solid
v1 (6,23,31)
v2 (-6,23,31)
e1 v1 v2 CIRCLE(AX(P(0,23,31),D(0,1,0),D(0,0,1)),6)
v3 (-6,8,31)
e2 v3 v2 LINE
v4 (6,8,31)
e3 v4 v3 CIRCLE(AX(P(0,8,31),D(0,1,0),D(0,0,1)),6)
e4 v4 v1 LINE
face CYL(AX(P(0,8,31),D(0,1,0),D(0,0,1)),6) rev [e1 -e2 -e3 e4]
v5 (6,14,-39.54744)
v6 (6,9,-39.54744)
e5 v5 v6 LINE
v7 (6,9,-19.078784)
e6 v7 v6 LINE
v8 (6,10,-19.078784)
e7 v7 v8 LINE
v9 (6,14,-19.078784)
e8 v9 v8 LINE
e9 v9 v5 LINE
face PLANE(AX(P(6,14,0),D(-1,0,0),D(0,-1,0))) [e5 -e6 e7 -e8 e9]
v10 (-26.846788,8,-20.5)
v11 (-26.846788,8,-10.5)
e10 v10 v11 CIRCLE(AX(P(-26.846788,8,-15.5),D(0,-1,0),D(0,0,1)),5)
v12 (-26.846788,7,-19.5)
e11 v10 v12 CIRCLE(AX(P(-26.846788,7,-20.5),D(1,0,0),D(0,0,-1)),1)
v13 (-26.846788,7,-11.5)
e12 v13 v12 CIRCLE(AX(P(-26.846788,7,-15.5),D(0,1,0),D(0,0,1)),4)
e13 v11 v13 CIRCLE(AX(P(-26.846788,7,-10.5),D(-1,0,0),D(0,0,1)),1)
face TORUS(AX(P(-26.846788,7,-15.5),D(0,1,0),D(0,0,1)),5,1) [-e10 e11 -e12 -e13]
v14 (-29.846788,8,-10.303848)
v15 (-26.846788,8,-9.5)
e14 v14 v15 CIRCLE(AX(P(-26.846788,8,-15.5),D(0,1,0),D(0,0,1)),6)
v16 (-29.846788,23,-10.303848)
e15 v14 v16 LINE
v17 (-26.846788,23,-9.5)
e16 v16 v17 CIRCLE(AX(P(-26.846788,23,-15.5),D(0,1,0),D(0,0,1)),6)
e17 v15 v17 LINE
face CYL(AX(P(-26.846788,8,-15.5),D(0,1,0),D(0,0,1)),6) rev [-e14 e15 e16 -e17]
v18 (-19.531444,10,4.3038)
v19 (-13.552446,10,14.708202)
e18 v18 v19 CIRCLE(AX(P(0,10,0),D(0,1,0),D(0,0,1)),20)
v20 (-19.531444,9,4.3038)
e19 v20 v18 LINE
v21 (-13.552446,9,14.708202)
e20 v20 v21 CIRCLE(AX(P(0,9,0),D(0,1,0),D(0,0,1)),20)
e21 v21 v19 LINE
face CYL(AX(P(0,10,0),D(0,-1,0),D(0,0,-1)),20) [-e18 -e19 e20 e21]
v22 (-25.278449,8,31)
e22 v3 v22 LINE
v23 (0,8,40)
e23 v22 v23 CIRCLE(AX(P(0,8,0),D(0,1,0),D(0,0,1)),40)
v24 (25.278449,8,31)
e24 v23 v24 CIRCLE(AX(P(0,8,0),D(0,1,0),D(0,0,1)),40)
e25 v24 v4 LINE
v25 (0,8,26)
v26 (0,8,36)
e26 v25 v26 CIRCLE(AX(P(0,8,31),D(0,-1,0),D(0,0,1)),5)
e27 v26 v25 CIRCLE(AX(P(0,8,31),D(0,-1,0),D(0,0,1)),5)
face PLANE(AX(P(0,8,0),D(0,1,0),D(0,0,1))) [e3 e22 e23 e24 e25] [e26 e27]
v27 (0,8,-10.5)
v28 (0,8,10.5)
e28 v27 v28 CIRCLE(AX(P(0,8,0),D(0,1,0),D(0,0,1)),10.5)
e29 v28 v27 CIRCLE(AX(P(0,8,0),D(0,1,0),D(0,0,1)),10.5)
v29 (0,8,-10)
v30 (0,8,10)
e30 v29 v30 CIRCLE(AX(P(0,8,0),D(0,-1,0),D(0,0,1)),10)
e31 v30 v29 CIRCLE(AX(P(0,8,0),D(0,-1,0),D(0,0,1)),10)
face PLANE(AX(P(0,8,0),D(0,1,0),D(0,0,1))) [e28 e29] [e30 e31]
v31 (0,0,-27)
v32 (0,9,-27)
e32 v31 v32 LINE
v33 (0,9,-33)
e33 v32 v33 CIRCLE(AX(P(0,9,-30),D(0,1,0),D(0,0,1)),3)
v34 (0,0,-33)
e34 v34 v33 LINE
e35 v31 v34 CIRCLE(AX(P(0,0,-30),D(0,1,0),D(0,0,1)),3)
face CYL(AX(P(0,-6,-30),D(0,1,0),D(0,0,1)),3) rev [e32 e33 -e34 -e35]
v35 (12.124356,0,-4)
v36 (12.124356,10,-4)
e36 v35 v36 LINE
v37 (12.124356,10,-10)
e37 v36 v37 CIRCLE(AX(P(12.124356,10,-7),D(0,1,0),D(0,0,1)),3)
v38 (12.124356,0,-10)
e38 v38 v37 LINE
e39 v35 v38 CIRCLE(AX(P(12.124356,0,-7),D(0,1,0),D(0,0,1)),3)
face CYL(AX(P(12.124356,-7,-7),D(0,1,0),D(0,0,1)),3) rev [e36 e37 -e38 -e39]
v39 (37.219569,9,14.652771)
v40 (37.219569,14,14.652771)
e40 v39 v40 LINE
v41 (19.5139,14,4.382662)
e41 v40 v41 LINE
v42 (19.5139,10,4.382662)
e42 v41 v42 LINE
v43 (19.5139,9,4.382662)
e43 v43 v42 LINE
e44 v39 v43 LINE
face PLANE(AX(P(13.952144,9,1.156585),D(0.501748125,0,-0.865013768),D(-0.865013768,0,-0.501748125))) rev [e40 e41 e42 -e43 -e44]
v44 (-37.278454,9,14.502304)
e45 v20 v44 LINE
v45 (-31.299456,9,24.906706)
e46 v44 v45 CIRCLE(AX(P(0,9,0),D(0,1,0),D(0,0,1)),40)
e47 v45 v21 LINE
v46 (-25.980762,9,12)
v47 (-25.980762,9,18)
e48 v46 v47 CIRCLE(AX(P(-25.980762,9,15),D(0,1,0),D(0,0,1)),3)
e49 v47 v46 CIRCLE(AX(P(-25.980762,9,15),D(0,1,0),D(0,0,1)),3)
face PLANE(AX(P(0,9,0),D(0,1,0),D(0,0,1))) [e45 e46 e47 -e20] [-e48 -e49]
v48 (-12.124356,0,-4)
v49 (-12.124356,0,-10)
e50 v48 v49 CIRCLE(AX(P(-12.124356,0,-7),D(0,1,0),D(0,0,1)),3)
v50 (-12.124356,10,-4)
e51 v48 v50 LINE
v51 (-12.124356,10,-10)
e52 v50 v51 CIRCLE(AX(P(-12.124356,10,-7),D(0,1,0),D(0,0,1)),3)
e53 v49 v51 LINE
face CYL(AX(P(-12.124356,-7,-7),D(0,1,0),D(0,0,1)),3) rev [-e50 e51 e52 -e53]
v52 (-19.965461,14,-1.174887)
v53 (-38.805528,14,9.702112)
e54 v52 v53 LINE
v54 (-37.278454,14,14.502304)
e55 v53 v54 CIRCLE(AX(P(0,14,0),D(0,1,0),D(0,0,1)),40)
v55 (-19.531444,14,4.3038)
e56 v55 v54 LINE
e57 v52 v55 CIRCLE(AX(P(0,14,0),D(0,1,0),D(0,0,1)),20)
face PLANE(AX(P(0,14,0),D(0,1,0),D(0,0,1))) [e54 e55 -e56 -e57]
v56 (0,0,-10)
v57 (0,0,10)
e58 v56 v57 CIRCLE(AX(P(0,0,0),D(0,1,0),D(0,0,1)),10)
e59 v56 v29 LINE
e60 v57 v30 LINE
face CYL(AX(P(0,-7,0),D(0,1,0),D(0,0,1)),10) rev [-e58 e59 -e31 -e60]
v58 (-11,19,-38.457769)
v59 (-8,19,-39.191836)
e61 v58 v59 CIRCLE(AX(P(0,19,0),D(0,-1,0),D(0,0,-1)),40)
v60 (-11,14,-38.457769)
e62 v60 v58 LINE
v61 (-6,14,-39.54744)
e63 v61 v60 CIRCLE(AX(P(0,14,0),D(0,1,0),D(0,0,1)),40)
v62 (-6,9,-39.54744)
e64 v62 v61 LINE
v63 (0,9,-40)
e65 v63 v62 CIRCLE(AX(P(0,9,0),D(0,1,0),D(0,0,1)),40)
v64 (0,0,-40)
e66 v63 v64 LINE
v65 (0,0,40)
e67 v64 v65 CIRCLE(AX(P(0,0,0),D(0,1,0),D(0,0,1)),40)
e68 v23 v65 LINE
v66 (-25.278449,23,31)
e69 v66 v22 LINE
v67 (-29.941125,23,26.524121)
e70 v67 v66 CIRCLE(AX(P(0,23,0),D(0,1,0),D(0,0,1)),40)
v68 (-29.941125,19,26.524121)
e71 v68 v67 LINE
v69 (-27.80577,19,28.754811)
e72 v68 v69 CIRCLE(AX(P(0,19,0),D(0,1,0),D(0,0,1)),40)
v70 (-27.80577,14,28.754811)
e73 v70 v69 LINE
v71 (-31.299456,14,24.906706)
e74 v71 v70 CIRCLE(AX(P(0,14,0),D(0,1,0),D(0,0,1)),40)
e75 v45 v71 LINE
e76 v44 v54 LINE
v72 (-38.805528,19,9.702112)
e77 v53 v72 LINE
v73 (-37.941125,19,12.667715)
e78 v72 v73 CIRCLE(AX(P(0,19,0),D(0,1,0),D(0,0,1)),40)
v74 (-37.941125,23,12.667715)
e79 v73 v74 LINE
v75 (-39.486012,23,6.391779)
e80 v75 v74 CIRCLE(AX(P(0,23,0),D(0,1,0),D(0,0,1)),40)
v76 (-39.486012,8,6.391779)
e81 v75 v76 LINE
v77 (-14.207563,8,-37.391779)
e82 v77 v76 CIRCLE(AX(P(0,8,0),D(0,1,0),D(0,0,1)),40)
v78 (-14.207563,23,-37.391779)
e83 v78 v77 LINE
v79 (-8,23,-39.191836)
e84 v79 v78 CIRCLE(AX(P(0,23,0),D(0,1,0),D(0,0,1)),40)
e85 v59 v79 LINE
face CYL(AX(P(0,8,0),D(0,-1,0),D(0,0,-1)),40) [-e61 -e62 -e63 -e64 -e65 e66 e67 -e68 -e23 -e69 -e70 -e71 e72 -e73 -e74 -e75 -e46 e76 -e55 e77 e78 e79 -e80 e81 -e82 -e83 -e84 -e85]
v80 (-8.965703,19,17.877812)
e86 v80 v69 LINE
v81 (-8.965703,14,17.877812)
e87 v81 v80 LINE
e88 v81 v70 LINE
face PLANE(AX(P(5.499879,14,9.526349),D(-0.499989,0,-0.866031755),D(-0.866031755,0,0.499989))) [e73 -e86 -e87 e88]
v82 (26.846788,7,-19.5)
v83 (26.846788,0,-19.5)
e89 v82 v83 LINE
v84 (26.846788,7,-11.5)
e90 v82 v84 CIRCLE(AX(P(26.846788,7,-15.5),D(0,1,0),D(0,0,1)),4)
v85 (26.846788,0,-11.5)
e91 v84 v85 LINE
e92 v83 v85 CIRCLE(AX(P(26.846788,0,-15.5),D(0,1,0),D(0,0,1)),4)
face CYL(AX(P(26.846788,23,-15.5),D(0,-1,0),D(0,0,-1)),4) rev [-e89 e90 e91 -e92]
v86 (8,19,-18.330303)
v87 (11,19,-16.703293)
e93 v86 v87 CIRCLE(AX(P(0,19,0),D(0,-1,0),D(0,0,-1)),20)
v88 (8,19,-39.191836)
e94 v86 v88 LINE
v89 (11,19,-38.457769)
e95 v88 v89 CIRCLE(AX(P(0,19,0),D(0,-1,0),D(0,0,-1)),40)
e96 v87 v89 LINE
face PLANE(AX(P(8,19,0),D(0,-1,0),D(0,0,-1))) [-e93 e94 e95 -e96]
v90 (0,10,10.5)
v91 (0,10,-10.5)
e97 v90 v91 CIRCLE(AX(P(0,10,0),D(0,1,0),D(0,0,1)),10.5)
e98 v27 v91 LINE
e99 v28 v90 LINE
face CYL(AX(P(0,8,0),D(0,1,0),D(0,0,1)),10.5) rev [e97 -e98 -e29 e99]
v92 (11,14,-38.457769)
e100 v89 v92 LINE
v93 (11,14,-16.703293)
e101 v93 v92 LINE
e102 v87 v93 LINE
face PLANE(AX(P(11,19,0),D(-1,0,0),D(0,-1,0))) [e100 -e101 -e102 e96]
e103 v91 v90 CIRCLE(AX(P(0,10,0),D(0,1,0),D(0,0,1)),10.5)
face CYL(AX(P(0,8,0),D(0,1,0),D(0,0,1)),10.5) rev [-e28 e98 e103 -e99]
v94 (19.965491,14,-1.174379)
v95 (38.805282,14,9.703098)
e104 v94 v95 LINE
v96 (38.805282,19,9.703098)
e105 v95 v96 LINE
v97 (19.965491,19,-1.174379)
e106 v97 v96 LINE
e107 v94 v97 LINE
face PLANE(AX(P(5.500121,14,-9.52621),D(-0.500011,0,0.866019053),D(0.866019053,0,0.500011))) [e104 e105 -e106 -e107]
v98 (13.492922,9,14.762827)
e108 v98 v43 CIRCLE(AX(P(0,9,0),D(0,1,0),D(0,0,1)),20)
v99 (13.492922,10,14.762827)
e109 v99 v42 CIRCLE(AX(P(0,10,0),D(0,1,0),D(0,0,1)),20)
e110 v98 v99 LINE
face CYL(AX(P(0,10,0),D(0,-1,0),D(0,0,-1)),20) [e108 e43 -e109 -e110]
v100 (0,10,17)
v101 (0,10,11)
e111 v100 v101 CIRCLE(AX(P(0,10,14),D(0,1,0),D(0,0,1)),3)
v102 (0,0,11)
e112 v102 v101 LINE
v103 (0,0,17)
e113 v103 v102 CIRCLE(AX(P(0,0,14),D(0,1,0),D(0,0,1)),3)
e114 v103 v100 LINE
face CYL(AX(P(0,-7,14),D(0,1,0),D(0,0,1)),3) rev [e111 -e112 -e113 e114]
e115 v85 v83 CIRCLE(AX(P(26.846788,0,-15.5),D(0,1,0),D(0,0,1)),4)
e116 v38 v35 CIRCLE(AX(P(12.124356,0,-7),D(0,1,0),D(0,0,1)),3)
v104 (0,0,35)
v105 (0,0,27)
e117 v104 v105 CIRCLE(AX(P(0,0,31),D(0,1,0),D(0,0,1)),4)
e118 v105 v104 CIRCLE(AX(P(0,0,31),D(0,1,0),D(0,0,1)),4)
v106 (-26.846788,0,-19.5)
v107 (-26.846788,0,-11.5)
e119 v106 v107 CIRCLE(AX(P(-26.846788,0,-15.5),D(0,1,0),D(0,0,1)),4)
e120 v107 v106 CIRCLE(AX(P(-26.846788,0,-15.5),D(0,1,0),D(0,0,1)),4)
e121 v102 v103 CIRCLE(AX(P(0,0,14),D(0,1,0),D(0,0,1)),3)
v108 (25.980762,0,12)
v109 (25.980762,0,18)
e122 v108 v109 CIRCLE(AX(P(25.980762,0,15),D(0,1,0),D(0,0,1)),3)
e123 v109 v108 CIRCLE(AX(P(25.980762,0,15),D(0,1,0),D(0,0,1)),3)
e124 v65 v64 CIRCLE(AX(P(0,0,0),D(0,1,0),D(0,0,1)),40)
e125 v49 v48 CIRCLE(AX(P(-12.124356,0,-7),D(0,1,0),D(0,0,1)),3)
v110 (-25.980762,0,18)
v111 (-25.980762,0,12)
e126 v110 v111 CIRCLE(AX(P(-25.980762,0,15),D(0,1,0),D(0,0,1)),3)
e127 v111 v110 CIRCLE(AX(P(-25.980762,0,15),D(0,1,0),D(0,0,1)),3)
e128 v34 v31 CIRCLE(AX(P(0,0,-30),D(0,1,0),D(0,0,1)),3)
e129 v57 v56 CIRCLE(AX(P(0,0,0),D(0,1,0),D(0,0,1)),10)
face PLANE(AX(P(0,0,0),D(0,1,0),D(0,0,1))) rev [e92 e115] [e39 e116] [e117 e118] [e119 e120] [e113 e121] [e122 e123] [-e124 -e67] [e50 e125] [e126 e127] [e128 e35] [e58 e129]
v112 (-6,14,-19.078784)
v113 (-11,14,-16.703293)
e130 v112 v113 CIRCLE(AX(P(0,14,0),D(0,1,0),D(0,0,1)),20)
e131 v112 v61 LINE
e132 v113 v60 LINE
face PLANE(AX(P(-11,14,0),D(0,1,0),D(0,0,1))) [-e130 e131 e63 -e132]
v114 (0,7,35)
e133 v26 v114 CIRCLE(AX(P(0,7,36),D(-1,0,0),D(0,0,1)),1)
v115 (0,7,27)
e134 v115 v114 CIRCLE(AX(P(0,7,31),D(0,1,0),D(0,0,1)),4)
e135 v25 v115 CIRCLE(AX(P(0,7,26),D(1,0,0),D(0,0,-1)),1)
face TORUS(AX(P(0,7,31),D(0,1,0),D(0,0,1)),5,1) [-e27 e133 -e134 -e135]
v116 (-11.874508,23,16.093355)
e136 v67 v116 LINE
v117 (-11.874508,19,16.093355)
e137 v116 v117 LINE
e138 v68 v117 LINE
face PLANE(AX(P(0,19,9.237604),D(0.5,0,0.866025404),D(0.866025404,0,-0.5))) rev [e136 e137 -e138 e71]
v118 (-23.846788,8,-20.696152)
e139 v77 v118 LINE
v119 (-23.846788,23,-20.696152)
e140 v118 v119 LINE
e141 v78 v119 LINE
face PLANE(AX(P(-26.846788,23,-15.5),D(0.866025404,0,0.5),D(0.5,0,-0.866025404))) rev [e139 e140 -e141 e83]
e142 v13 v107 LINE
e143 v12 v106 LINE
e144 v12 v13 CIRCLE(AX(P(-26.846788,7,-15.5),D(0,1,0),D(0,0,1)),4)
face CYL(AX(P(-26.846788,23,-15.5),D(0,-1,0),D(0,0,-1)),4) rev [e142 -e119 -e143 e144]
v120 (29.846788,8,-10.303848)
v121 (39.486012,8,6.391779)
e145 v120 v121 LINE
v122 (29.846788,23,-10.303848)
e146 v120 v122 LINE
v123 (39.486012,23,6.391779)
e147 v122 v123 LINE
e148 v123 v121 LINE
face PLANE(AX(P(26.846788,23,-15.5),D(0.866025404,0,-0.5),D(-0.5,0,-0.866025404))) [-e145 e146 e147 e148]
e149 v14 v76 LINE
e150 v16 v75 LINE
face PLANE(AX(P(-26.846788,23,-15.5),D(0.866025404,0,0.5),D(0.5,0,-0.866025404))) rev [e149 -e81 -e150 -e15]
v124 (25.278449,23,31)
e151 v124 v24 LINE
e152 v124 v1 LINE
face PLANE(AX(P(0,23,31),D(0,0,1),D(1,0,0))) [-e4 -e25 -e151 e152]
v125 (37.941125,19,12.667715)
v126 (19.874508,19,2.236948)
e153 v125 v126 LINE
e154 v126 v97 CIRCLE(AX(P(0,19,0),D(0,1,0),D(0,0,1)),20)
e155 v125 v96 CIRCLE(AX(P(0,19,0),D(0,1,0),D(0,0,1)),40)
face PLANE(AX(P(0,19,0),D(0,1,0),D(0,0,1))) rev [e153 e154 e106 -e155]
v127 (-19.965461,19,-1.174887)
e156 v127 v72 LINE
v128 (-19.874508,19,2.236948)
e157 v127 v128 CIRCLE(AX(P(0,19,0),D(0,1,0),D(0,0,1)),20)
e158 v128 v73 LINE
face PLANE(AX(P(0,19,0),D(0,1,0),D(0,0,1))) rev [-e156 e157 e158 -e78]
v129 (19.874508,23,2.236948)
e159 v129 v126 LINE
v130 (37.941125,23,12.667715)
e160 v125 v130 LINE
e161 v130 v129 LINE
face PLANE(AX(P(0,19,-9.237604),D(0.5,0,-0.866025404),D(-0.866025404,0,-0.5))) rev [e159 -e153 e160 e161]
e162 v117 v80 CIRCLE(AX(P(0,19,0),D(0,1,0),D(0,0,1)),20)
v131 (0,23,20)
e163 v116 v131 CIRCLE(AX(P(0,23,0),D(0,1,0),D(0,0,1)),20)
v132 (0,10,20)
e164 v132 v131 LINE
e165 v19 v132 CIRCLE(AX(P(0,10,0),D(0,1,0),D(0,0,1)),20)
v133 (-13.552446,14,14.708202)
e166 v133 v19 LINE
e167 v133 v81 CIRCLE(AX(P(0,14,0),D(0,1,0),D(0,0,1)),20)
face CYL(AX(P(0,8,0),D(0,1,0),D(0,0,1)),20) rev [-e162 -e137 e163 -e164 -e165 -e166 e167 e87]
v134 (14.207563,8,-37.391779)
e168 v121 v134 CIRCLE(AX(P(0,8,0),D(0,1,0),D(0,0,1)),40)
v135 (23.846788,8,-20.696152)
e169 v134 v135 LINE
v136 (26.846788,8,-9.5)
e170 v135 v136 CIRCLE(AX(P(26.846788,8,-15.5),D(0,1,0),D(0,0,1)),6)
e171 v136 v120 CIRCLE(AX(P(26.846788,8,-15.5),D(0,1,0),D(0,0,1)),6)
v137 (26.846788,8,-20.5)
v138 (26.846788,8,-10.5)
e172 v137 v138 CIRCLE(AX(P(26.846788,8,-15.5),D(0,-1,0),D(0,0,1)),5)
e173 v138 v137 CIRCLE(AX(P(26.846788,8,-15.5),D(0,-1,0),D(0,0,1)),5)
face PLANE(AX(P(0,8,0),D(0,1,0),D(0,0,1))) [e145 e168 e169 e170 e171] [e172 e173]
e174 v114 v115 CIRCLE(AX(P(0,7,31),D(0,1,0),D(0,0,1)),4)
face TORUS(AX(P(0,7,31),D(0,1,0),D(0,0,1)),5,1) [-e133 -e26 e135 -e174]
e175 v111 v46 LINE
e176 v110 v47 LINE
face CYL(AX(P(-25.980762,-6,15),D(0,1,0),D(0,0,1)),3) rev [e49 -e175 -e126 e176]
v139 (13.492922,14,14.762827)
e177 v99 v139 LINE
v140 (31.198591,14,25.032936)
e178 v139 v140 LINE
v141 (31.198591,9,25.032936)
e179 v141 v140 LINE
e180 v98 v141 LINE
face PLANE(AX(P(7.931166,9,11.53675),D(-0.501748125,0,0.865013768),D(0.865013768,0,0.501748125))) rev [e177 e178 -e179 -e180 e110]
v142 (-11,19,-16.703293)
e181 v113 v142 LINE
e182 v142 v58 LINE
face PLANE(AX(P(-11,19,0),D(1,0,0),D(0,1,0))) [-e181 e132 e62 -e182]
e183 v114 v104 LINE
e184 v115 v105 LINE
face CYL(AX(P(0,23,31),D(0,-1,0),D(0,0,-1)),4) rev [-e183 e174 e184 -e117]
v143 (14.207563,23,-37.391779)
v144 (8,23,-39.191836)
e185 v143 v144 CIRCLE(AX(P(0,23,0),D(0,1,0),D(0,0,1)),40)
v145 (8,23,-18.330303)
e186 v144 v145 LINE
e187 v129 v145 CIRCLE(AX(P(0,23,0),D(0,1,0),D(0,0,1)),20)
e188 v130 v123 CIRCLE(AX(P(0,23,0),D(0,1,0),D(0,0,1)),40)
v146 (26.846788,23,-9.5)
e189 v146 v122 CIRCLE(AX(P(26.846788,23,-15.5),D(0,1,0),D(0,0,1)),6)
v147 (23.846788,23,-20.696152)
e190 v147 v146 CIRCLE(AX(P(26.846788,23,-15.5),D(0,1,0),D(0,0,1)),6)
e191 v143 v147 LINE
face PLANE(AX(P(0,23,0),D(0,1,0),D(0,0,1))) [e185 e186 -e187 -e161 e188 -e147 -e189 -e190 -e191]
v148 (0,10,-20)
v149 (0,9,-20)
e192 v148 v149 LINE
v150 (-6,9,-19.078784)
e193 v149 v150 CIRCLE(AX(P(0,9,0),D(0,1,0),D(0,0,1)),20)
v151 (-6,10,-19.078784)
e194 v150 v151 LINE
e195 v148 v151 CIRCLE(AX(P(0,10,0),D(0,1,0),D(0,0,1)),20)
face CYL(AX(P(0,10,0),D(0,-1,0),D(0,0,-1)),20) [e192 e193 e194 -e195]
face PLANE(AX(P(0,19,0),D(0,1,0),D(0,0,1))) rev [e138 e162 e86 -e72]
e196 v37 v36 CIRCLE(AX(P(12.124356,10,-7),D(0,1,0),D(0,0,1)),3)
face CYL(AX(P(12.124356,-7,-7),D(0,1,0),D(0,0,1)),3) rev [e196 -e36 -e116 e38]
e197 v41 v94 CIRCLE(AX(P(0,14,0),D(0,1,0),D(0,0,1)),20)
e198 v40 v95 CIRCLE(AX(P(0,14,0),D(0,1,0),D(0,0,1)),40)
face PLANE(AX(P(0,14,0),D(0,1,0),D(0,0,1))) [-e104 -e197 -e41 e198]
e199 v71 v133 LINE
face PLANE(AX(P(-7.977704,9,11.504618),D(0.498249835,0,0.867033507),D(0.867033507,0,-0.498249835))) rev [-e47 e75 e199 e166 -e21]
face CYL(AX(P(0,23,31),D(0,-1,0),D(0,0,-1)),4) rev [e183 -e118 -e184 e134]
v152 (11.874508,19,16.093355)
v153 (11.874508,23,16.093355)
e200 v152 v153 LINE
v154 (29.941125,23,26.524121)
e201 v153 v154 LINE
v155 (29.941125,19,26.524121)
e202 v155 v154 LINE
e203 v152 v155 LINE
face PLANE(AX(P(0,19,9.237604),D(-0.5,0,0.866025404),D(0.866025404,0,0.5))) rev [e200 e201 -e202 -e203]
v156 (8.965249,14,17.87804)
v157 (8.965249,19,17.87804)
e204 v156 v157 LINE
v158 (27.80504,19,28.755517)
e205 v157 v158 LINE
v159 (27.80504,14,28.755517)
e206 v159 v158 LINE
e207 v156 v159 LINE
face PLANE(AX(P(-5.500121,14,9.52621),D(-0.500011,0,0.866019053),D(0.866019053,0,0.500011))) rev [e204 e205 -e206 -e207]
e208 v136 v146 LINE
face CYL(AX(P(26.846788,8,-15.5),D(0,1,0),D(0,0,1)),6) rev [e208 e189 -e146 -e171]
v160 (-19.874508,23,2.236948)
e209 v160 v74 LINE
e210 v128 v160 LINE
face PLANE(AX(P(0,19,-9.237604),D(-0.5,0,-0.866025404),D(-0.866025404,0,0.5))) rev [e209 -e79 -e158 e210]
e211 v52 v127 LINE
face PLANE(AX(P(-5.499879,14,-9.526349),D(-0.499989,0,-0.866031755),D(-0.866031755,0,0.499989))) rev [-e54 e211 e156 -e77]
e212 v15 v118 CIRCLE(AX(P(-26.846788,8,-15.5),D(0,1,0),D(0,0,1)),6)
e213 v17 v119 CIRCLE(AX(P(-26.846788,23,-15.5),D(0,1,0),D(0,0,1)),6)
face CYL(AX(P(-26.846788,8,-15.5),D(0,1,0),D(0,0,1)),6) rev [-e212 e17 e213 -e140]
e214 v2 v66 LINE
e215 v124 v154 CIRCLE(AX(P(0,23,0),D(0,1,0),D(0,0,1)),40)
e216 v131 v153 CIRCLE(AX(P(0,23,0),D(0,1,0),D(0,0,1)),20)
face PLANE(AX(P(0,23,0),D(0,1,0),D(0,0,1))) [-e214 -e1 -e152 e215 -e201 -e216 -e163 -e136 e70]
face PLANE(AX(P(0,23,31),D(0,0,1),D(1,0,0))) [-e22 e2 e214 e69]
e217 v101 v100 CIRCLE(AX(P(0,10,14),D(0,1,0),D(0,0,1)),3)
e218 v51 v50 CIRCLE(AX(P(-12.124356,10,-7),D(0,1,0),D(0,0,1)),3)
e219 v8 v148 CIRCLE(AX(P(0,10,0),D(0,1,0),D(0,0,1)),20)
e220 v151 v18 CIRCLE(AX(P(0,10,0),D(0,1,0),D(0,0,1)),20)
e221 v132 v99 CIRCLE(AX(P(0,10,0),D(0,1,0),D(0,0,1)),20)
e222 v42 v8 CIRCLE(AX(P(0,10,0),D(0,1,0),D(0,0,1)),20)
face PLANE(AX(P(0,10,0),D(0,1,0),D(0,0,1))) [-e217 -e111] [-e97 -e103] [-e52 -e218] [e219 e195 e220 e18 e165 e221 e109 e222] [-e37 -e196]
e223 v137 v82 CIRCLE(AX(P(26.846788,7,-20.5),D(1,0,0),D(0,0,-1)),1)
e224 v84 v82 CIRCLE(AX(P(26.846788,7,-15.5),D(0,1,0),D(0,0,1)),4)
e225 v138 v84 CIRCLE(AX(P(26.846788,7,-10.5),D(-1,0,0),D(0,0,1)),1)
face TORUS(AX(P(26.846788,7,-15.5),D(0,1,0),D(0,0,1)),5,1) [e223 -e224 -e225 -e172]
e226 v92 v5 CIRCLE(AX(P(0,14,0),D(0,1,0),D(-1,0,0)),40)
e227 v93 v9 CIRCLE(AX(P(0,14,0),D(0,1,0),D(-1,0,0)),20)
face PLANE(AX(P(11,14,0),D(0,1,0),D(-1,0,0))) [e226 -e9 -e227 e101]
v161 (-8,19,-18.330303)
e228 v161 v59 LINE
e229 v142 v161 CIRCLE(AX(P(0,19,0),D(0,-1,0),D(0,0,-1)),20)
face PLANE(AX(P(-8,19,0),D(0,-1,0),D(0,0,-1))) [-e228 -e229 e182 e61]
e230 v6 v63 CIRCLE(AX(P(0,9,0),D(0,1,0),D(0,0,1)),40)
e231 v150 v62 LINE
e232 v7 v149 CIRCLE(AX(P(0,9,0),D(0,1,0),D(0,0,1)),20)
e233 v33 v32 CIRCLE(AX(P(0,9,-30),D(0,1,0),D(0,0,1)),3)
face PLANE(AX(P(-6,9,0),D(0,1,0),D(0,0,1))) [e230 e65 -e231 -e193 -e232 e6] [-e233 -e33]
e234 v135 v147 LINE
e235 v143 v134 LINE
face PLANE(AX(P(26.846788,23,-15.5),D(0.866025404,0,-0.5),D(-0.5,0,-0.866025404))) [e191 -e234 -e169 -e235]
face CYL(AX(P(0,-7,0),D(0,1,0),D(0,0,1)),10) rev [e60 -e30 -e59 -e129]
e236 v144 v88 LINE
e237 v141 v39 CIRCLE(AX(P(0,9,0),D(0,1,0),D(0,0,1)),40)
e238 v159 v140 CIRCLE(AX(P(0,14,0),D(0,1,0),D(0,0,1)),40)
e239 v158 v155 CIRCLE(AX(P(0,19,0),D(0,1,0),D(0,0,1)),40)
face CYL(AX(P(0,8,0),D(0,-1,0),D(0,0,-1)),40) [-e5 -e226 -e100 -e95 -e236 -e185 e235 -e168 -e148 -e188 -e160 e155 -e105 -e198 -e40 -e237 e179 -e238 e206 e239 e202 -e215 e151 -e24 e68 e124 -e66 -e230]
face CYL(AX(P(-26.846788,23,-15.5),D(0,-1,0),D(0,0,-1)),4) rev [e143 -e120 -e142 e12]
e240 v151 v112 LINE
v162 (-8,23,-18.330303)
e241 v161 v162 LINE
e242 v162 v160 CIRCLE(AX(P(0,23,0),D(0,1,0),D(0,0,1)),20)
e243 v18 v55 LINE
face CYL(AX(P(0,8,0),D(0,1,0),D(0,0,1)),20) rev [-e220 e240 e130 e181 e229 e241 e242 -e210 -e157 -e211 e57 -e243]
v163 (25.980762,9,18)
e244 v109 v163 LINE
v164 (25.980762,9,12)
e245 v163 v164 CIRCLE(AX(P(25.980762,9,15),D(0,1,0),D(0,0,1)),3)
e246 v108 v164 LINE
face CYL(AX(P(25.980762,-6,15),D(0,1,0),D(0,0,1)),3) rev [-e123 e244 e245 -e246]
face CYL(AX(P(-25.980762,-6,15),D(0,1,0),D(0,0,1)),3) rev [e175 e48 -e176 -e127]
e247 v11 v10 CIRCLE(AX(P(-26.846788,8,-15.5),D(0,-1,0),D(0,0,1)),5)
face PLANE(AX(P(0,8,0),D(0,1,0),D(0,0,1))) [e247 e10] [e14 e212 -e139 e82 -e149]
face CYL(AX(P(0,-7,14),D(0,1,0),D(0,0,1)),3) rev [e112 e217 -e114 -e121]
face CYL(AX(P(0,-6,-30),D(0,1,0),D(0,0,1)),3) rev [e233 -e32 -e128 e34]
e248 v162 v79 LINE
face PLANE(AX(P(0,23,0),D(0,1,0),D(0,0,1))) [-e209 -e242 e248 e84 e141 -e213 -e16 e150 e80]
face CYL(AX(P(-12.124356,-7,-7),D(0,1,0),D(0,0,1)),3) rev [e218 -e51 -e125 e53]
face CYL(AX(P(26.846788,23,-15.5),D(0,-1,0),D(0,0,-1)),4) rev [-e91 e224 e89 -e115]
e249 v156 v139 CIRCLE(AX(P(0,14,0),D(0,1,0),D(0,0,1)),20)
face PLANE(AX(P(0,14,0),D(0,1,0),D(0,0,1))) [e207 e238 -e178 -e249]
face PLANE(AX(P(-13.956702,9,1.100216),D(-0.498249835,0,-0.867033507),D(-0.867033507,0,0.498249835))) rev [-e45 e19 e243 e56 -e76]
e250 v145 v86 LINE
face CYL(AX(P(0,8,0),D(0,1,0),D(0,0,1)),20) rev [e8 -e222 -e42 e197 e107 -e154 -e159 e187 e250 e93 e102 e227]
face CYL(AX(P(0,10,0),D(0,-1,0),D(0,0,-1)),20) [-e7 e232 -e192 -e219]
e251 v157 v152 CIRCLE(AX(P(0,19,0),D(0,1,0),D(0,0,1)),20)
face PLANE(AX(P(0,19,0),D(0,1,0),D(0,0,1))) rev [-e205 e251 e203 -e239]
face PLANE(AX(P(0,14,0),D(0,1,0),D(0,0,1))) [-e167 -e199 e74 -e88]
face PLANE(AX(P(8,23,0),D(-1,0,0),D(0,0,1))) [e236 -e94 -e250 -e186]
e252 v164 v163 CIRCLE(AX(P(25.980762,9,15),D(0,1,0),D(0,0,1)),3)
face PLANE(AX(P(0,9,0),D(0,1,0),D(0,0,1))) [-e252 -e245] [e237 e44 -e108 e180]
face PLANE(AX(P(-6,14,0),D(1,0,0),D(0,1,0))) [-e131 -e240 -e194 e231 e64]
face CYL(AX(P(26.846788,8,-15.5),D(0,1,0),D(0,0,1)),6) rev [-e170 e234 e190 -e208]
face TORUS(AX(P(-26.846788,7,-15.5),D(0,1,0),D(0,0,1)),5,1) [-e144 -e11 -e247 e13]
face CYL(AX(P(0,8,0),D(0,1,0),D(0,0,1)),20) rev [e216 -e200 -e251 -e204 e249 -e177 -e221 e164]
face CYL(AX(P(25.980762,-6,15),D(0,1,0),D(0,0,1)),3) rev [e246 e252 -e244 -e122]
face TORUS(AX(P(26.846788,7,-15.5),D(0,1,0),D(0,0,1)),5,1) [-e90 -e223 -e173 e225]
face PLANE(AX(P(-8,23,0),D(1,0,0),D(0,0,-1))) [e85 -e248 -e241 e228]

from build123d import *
from build123d.topology import SkipClean

# Parameters (mm, degrees)
FLANGE_DISC_SKETCH_R           = 40
FLANGE_DISC_80_DEPTH           = 8
JAW_GUIDE_BOSSES_SKETCH_R      = 14
JAW_GUIDE_BOSSES_DEPTH         = 15
TRIANGULAR_START               = -30
TRIANGULAR_CENTRE_CUT_SKETCH_R = 4
TRIANGULAR_CENTRE_CUT_DEPTH    = 30
HEX_CUT_DEPTH                  = 15
JAW_SLOT_PROFILE_CUT_DEPTH     = 40
JAW_START                      = -4
JAW_POCKET_CUT_DEPTH           = 4
JAW_START_2                    = -5
JAW_GROOVE_CUT_A_DEPTH         = 5
JAW_GROOVE_CUT_B_DEPTH         = 5
CENTRE_BORE_SKETCH_R           = 20
CENTRE_BORE_40_DEPTH           = 15
THROUGH_BORE_SKETCH_R          = 10
THROUGH_BORE_20_DEPTH          = 15
FLANGE_HOLES_SKETCH_R          = 3
FLANGE_HOLES_3X_6_DEPTH        = 15
HUB_START                      = 2
HUB_RING_SKETCH_R              = 20
HUB_RING_SKETCH_R_2            = 10
HUB_RING_SKETCH_R_3            = 3
HUB_RING_DEPTH                 = 2
EDGE_FILLET_R1_A_R             = 1
EDGE_FILLET_R1_B_R             = 1
JAW_HOLES_SKETCH_R             = 3
JAW_HOLES_3X_6_DEPTH           = 15
COUNTERBORE_SKETCH_R           = 10.5
COUNTERBORE_21_DEPTH           = 2


with BuildPart() as part:
    # Flange Disc Sketch → Flange Disc Ø80 (new body)
    with BuildSketch(Plane(origin=(0, 0, 0), x_dir=(1, 0, 0), z_dir=(0, 1, 0))):
        with Locations(Location((0, 0, 0), (0, 0, 270))):
            Circle(FLANGE_DISC_SKETCH_R)
    extrude(amount=FLANGE_DISC_80_DEPTH)

    # Jaw Guide Bosses Sketch → Jaw Guide Bosses (add)
    with BuildSketch(Plane(origin=(0, 8, 0), x_dir=(1, 0, 0), z_dir=(0, 1, 0))):
        with BuildLine():
            ThreePointArc((-22.846787517, 15.5), (-24.846787517, 12.035898385), (-28.846787517, 12.035898385))
            Line((-28.846787517, 12.035898385), (-39.486012177, -6.391779279))
            ThreePointArc((-39.486012177, -6.391779279), (-34.641016151, -20), (-25.27844932, -31))
            Line((-25.27844932, -31), (-4, -31))
            ThreePointArc((-4, -31), (0, -27), (4, -31))
            Line((4, -31), (25.27844932, -31))
            ThreePointArc((25.27844932, -31), (34.641016151, -20), (39.486012177, -6.391779279))
            Line((39.486012177, -6.391779279), (28.846787517, 12.035898385))
            ThreePointArc((28.846787517, 12.035898385), (23.382685902, 13.5), (24.846787517, 18.964101615))
            Line((24.846787517, 18.964101615), (14.207562858, 37.391779279))
            ThreePointArc((14.207562858, 37.391779279), (0, 40), (-14.207562858, 37.391779279))
            Line((-14.207562858, 37.391779279), (-24.846787517, 18.964101615))
            ThreePointArc((-24.846787517, 18.964101615), (-23.382685902, 17.5), (-22.846787517, 15.5))
        make_face()
        with Locations(Location((0, 0, 0), (0, 0, 270))):
            Circle(JAW_GUIDE_BOSSES_SKETCH_R, mode=Mode.SUBTRACT)
    extrude(amount=JAW_GUIDE_BOSSES_DEPTH)

    # Triangular Centre Cut Sketch → Triangular Centre Cut (cut)
    with SkipClean():  # the faces are left unmerged after this step: merging them gives an invalid solid
        with BuildSketch(Plane(origin=(0, 23, 0), x_dir=(1, 0, 0), z_dir=(0, 1, 0)).offset(TRIANGULAR_START)):
            with Locations(Location((-26.846787517, 15.5, 0), (0, 0, 60))):
                Circle(TRIANGULAR_CENTRE_CUT_SKETCH_R)
            with Locations(Location((26.846787517, 15.5, 0), (0, 0, 120))):
                Circle(TRIANGULAR_CENTRE_CUT_SKETCH_R)
            with Locations((0, -31)):
                Circle(TRIANGULAR_CENTRE_CUT_SKETCH_R)
        extrude(amount=TRIANGULAR_CENTRE_CUT_DEPTH, mode=Mode.SUBTRACT)

    # Hex Cut Sketch → Hex Cut (cut)
    with BuildSketch(Plane(origin=(0, 23, 0), x_dir=(1, 0, 0), z_dir=(0, 1, 0))):
        with BuildLine():
            Line((-29.846787517, 10.303847577), (-23.846787517, 20.696152423))
            ThreePointArc((-23.846787517, 20.696152423), (-21.650635095, 12.5), (-29.846787517, 10.303847577))
        make_face()
        with BuildLine():
            Line((23.846787517, 20.696152423), (29.846787517, 10.303847577))
            ThreePointArc((29.846787517, 10.303847577), (21.650635095, 12.5), (23.846787517, 20.696152423))
        make_face()
        with BuildLine():
            Line((-6, -31), (6, -31))
            ThreePointArc((6, -31), (0, -25), (-6, -31))
        make_face()
    extrude(amount=-HEX_CUT_DEPTH, mode=Mode.SUBTRACT)

    # Jaw Slot Profile Sketch → Jaw Slot Profile Cut (cut)
    with BuildSketch(Plane.XY.offset(-40)):
        Polygon((8, 23), (-8, 23), (-8, 19), (-11, 19), (-11, 14), (-6, 14), (-6, 9), (6, 9), (6, 14), (11, 14), (11, 19), (8, 19), align=None)
    extrude(amount=JAW_SLOT_PROFILE_CUT_DEPTH, mode=Mode.SUBTRACT)

    # Jaw Pocket Sketch → Jaw Pocket Cut (cut)
    with BuildSketch(Plane(origin=(0, 23, 0), x_dir=(1, 0, 0), z_dir=(0, 1, 0)).offset(JAW_START)):
        with BuildLine():
            Line((0, 9.237604307), (37.941125497, -12.667714712))
            ThreePointArc((37.941125497, -12.667714712), (34.641016151, -20), (29.941125497, -26.524121173))
            Line((29.941125497, -26.524121173), (0, -9.237604307))
            Line((0, -9.237604307), (-29.941125497, -26.524121173))
            ThreePointArc((-29.941125497, -26.524121173), (-34.641016151, -20), (-37.941125497, -12.667714712))
            Line((-37.941125497, -12.667714712), (0, 9.237604307))
        make_face()
    extrude(amount=JAW_POCKET_CUT_DEPTH, mode=Mode.SUBTRACT)

    # Jaw Groove Sketch A → Jaw Groove Cut A (cut)
    with BuildSketch(Plane(origin=(0, 19, 0), x_dir=(1, 0, 0), z_dir=(0, 1, 0)).offset(JAW_START_2)):
        with BuildLine():
            Line((-27.805770218, -28.754810773), (-2.000176006, -13.856381055))
            ThreePointArc((-2.000176006, -13.856381055), (-4.018838324, -13.410776955), (-5.949874371, -12.672765877))
            Line((-5.949874371, -12.672765877), (-29.941125497, -26.524121173))
            ThreePointArc((-29.941125497, -26.524121173), (-28.894982007, -27.660079805), (-27.805770218, -28.754810773))
        make_face()
        with BuildLine():
            Line((-37.941125497, -12.667714712), (-13.949874371, 1.183640584))
            ThreePointArc((-13.949874371, 1.183640584), (-13.623451724, 3.225145443), (-12.999933997, 5.196317551))
            Line((-12.999933997, 5.196317551), (-38.805528208, -9.702112168))
            ThreePointArc((-38.805528208, -9.702112168), (-38.401964967, -11.19326077), (-37.941125497, -12.667714712))
        make_face()
        with BuildLine():
            ThreePointArc((-5.949874371, -12.672765877), (-12.124355653, -7), (-13.949874371, 1.183640584))
            Line((-13.949874371, 1.183640584), (-37.941125497, -12.667714712))
            ThreePointArc((-37.941125497, -12.667714712), (-34.641016151, -20), (-29.941125497, -26.524121173))
            Line((-29.941125497, -26.524121173), (-5.949874371, -12.672765877))
        make_face()
        with BuildLine():
            Line((38.805281719, -9.703097994), (13.000066001, 5.195987294))
            ThreePointArc((13.000066001, 5.195987294), (12.124266737, -7.000154005), (1.999823994, -13.856431864))
            Line((1.999823994, -13.856431864), (27.805039711, -28.755517151))
            ThreePointArc((27.805039711, -28.755517151), (34.640762105, -20.000440015), (38.805281719, -9.703097994))
        make_face()
    extrude(amount=JAW_GROOVE_CUT_A_DEPTH, mode=Mode.SUBTRACT)

    # Jaw Groove Sketch B → Jaw Groove Cut B (cut)
    with BuildSketch(Plane(origin=(0, 14, 0), x_dir=(1, 0, 0), z_dir=(0, 1, 0)).offset(JAW_START_2)):
        with BuildLine():
            Line((13.952143608, -1.156584943), (37.219568724, -14.652771205))
            ThreePointArc((37.219568724, -14.652771205), (34.600550719, -20.069925011), (31.198591221, -25.03293642))
            Line((31.198591221, -25.03293642), (7.931166105, -11.536750158))
            ThreePointArc((7.931166105, -11.536750158), (12.110192752, -7.024473754), (13.952143608, -1.156584943))
        make_face()
        with BuildLine():
            Line((-13.956701767, -1.10021625), (-37.278454482, -14.50230435))
            ThreePointArc((-37.278454482, -14.50230435), (-34.681340271, -19.929993402), (-31.299456461, -24.906706431))
            Line((-31.299456461, -24.906706431), (-7.977703746, -11.504618331))
            ThreePointArc((-7.977703746, -11.504618331), (-12.138469095, -6.975497691), (-13.956701767, -1.10021625))
        make_face()
    extrude(amount=JAW_GROOVE_CUT_B_DEPTH, mode=Mode.SUBTRACT)

    # Centre Bore Sketch → Centre Bore Ø40 (cut)
    with BuildSketch(Plane(origin=(0, 23, 0), x_dir=(1, 0, 0), z_dir=(0, 1, 0))):
        with Locations(Location((0, 0, 0), (0, 0, 270))):
            Circle(CENTRE_BORE_SKETCH_R)
    extrude(amount=-CENTRE_BORE_40_DEPTH, mode=Mode.SUBTRACT)

    # Through Bore Sketch → Through Bore Ø20 (cut)
    with BuildSketch(Plane(origin=(0, 8, 0), x_dir=(1, 0, 0), z_dir=(0, 1, 0))):
        with Locations(Location((0, 0, 0), (0, 0, 270))):
            Circle(THROUGH_BORE_SKETCH_R)
    extrude(amount=-THROUGH_BORE_20_DEPTH, mode=Mode.SUBTRACT)

    # Flange Holes Sketch → Flange Holes 3xØ6 (cut)
    with BuildSketch(Plane(origin=(0, 8, 0), x_dir=(1, 0, 0), z_dir=(0, 1, 0))):
        with Locations(Location((0, -14, 0), (0, 0, 270))):
            Circle(FLANGE_HOLES_SKETCH_R)
        with Locations(Location((-12.124355653, 7, 0), (0, 0, 270))):
            Circle(FLANGE_HOLES_SKETCH_R)
        with Locations(Location((12.124355653, 7, 0), (0, 0, 270))):
            Circle(FLANGE_HOLES_SKETCH_R)
    extrude(amount=-FLANGE_HOLES_3X_6_DEPTH, mode=Mode.SUBTRACT)

    # Hub Ring Sketch → Hub Ring (add)
    with BuildSketch(Plane(origin=(0, 8, 0), x_dir=(1, 0, 0), z_dir=(0, 1, 0)).offset(HUB_START)):
        Circle(HUB_RING_SKETCH_R)
        with Locations(Location((0, 0, 0), (0, 0, 270))):
            Circle(HUB_RING_SKETCH_R_2, mode=Mode.SUBTRACT)
        with Locations(Location((-12.124355653, 7, 0), (0, 0, 270))):
            Circle(HUB_RING_SKETCH_R_3, mode=Mode.SUBTRACT)
        with Locations(Location((12.124355653, 7, 0), (0, 0, 270))):
            Circle(HUB_RING_SKETCH_R_3, mode=Mode.SUBTRACT)
        with Locations(Location((0, -14, 0), (0, 0, 270))):
            Circle(HUB_RING_SKETCH_R_3, mode=Mode.SUBTRACT)
    extrude(amount=-HUB_RING_DEPTH)

    # Edge Fillet R1 A
    edge_fillet_r1_a_edges = [part.edges().sort_by_distance(p)[0] for p in [
        (28.846787517, 8, -12.035898385),
    ]]
    fillet(edge_fillet_r1_a_edges, radius=EDGE_FILLET_R1_A_R)

    # Edge Fillet R1 B
    edge_fillet_r1_b_edges = [part.edges().sort_by_distance(p)[0] for p in [
        (-28.846787517, 8, -12.035898385),
        (-4, 8, 31),
    ]]
    fillet(edge_fillet_r1_b_edges, radius=EDGE_FILLET_R1_B_R)

    # Jaw Holes Sketch → Jaw Holes 3xØ6 (cut)
    with BuildSketch(Plane(origin=(0, 9, 0), x_dir=(1, 0, 0), z_dir=(0, 1, 0))):
        with Locations(Location((0, 30, 0), (0, 0, 270))):
            Circle(JAW_HOLES_SKETCH_R)
        with Locations(Location((25.980762114, -15, 0), (0, 0, 270))):
            Circle(JAW_HOLES_SKETCH_R)
        with Locations(Location((-25.980762114, -15, 0), (0, 0, 270))):
            Circle(JAW_HOLES_SKETCH_R)
    extrude(amount=-JAW_HOLES_3X_6_DEPTH, mode=Mode.SUBTRACT)

    # Counterbore Sketch → Counterbore Ø21 (cut)
    with BuildSketch(Plane(origin=(0, 10, 0), x_dir=(1, 0, 0), z_dir=(0, 1, 0))):
        with Locations(Location((0, 0, 0), (0, 0, 270))):
            Circle(COUNTERBORE_SKETCH_R)
    extrude(amount=-COUNTERBORE_21_DEPTH, mode=Mode.SUBTRACT)


solid = part.part
